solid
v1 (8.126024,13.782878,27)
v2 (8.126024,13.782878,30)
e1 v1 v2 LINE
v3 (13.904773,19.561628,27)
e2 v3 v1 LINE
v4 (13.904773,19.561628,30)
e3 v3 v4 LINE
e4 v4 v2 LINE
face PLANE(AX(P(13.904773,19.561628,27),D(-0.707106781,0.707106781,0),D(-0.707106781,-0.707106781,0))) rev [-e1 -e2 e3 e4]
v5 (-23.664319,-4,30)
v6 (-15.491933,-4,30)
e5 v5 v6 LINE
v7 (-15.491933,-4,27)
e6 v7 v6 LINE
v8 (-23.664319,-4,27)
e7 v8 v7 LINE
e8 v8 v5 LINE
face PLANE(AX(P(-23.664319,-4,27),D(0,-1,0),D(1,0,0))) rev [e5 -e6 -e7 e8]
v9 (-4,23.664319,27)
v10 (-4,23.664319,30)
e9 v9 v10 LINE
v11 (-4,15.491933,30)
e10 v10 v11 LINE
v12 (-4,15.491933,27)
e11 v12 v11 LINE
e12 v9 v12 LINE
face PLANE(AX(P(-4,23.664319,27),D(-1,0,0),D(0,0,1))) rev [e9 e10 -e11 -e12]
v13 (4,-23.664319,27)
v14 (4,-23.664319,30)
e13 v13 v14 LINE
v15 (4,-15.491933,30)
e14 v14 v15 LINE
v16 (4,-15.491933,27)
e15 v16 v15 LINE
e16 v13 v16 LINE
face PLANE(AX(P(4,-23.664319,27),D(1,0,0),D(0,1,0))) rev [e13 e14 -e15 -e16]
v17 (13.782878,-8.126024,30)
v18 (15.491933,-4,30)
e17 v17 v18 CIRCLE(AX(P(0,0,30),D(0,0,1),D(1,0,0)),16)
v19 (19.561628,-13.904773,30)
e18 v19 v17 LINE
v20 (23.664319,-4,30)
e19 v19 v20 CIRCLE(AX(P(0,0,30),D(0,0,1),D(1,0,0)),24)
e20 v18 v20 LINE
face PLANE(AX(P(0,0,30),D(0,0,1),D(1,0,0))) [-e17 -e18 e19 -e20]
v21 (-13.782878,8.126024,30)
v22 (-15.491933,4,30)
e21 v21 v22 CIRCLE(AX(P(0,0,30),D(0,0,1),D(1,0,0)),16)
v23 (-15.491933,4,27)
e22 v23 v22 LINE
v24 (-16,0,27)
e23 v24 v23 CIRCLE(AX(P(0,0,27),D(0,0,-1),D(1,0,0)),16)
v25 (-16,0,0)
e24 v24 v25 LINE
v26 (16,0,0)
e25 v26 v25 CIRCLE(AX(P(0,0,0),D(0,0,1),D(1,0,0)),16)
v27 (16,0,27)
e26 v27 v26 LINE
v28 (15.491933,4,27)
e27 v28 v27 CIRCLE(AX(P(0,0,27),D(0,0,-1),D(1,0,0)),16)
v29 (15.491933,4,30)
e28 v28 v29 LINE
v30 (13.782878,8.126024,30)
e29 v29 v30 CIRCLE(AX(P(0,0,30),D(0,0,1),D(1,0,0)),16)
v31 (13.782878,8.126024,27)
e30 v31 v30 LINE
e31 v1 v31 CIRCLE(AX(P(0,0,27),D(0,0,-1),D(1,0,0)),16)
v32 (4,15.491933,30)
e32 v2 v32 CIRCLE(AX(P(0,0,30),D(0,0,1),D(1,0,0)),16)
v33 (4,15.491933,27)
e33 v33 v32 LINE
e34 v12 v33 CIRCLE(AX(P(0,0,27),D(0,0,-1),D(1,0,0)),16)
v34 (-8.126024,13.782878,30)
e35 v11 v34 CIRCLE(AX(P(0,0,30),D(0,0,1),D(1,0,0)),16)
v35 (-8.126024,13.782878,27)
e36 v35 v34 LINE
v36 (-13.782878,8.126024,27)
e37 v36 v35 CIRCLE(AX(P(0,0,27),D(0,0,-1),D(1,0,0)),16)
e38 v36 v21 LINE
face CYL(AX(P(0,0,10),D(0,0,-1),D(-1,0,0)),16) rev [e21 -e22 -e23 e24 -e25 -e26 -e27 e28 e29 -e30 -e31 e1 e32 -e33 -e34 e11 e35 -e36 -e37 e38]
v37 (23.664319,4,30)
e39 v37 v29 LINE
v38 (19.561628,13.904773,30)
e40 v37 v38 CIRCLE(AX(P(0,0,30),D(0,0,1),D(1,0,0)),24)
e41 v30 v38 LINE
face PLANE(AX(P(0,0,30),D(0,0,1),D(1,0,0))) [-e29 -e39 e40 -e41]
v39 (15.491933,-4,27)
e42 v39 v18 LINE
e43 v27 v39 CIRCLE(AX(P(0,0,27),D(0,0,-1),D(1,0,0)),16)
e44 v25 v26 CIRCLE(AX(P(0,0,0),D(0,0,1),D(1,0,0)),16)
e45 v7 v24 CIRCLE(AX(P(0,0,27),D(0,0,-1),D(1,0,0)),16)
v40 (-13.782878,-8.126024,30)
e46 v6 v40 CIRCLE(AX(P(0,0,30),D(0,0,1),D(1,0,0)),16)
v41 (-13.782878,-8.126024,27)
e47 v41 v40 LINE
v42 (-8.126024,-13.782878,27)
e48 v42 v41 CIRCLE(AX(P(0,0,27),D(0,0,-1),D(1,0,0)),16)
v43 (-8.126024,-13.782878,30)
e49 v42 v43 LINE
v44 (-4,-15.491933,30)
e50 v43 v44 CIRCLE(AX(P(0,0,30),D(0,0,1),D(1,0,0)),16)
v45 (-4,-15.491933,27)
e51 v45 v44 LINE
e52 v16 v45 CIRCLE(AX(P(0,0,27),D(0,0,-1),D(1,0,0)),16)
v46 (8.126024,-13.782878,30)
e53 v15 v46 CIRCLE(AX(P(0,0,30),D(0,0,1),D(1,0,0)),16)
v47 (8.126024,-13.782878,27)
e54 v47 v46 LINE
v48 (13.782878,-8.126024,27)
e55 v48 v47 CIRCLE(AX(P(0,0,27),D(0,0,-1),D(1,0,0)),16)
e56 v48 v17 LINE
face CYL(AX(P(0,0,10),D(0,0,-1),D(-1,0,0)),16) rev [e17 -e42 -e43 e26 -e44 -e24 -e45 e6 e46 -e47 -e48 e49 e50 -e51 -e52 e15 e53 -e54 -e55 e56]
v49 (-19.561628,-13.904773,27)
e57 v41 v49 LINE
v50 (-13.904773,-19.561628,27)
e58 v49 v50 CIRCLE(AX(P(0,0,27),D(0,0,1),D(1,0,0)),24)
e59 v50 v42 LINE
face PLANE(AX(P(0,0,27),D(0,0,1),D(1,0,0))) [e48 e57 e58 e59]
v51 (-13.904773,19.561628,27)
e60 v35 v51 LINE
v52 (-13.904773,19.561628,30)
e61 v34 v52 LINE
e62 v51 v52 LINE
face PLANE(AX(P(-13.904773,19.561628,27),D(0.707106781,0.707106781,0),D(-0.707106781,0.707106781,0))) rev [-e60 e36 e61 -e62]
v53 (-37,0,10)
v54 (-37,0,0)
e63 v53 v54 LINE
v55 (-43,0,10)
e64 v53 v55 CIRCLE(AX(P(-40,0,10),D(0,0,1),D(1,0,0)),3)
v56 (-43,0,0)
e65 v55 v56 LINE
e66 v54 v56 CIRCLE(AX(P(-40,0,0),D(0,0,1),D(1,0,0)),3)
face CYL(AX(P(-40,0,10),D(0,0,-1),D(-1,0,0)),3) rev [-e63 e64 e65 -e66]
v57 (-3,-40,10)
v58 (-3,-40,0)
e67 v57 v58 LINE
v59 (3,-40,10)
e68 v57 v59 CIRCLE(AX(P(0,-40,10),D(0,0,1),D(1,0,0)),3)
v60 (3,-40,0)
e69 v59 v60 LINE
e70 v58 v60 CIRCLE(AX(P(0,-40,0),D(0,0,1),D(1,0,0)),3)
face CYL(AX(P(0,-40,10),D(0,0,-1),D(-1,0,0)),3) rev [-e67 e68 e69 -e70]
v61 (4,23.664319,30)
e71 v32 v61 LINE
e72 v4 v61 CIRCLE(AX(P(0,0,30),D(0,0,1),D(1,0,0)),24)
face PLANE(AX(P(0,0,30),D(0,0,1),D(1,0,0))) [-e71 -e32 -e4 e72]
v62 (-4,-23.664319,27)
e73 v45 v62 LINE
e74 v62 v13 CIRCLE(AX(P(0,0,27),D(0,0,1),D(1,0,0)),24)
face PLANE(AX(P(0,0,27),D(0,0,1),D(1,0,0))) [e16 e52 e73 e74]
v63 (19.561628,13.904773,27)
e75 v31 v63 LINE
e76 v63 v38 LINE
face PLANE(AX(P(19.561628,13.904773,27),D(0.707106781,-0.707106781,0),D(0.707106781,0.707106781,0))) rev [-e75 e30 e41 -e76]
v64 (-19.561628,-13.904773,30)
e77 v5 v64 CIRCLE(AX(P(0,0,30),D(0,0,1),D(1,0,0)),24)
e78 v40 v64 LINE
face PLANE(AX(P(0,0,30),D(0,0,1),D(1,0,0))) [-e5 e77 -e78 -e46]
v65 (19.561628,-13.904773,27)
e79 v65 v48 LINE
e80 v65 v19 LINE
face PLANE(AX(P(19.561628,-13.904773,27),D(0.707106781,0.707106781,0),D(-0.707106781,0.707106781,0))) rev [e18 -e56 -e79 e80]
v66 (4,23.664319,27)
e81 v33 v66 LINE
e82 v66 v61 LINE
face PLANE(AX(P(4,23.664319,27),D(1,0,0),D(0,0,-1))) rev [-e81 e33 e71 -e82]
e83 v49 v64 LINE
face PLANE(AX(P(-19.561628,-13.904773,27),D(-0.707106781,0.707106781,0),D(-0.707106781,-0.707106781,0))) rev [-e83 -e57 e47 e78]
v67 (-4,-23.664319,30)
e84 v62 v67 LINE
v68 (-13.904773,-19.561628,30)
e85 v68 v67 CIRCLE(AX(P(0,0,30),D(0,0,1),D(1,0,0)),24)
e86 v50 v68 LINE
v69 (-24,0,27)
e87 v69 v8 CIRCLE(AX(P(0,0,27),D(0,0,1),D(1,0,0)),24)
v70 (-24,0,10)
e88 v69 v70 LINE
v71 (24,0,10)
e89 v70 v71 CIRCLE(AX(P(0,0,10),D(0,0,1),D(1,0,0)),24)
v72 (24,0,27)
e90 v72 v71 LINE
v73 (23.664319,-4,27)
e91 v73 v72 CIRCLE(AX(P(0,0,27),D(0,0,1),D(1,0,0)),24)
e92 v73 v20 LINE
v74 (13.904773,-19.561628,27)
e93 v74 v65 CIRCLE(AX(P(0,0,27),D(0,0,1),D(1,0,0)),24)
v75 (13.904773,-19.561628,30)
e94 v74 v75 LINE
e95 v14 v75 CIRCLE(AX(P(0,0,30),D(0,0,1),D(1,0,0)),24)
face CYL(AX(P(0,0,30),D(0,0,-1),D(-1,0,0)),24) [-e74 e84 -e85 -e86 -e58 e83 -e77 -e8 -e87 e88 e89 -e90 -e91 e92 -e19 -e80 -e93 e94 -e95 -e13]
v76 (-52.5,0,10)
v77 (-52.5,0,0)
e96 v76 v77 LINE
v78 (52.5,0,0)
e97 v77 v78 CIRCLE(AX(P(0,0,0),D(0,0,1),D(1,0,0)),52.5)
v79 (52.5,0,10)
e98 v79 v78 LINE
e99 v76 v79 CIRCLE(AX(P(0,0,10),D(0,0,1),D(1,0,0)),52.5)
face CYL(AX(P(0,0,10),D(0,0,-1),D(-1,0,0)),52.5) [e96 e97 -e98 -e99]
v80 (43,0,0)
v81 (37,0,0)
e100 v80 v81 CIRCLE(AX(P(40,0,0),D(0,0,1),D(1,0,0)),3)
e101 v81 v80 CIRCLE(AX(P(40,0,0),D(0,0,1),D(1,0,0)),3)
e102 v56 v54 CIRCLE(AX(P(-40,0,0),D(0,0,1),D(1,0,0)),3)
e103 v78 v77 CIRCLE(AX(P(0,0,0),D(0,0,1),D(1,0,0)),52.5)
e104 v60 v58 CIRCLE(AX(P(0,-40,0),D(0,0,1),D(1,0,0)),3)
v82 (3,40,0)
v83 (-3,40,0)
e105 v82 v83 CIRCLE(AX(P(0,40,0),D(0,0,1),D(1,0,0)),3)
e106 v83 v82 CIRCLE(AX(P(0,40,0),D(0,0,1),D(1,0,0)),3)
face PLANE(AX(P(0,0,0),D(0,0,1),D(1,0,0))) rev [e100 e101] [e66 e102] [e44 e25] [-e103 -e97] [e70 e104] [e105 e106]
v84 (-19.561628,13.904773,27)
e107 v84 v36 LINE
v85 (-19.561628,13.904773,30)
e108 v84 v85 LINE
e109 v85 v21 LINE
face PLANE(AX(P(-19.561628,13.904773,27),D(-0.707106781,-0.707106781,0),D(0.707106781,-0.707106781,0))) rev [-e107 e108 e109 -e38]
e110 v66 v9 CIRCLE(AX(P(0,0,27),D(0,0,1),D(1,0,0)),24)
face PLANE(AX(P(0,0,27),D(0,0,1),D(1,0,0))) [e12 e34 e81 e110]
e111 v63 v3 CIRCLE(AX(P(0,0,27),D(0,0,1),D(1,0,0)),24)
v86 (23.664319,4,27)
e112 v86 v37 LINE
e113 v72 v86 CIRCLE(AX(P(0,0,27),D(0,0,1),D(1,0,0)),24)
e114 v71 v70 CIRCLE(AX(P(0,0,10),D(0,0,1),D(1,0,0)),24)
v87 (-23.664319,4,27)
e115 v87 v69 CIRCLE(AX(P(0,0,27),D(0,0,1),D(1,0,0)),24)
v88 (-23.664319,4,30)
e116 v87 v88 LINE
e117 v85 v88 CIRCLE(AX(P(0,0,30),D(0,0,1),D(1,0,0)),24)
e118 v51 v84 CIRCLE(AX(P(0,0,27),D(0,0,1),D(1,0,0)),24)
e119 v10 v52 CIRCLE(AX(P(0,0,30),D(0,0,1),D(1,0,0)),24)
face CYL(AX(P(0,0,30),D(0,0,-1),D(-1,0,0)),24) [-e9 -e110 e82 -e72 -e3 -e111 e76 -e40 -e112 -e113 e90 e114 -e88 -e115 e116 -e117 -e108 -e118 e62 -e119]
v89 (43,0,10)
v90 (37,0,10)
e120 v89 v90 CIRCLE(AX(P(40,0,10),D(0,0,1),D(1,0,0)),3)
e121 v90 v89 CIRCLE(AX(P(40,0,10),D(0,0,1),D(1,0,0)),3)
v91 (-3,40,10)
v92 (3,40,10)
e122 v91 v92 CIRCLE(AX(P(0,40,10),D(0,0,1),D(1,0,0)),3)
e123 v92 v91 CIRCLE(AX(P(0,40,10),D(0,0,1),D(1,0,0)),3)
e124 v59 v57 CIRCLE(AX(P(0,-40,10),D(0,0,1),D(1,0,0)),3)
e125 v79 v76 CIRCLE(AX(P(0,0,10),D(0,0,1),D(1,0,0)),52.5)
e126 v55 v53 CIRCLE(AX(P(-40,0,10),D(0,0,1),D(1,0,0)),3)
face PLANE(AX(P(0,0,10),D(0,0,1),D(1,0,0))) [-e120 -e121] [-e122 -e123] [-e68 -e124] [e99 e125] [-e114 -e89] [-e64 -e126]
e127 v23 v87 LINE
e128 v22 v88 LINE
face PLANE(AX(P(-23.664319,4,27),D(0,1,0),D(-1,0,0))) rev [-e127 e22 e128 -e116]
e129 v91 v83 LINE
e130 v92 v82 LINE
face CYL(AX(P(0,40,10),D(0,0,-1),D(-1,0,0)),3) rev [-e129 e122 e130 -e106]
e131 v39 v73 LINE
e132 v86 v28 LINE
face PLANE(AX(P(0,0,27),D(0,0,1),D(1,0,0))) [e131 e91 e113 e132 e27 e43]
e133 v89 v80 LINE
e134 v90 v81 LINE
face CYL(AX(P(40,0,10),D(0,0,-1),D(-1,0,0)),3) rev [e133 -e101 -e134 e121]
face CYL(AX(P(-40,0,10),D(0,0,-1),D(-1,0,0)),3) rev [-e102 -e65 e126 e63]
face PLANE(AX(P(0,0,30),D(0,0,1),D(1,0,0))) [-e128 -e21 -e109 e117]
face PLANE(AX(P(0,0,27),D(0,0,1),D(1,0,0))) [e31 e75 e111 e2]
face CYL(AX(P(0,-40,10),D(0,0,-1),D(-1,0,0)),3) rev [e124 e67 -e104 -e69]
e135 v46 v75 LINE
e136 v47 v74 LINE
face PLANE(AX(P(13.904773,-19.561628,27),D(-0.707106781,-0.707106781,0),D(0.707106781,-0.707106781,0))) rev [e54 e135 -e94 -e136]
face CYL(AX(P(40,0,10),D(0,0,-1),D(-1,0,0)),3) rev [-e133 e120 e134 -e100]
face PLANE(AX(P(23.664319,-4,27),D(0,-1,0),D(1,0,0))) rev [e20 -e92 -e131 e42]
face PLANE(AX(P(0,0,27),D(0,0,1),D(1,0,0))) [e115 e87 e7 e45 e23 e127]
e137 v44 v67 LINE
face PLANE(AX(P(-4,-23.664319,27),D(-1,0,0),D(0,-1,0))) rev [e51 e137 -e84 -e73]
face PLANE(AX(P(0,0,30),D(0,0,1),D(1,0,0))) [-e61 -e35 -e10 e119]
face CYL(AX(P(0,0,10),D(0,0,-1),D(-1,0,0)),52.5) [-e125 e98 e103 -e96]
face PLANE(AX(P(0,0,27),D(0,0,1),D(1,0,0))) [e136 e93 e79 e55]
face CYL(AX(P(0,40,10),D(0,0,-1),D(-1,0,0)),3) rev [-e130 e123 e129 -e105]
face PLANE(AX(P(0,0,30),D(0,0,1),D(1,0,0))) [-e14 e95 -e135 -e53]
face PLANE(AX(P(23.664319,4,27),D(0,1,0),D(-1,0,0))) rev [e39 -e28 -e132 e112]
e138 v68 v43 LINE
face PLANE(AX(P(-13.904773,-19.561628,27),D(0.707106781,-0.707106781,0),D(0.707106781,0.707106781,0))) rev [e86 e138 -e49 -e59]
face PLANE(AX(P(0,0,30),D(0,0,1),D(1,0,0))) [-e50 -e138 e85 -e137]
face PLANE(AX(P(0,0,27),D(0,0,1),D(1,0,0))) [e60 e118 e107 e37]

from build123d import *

# Parameters (mm, degrees)
SKETCH_1_R          = 52.5
SKETCH_1_R_2        = 16
SKETCH_1_R_3        = 3
EXTRUDE_1_DEPTH     = 10
SKETCH_2_R          = 24
SKETCH_2_R_2        = 16
EXTRUDE_2_DEPTH     = 20
CUT_EXTRUDE_START   = -3
CUT_EXTRUDE_2_DEPTH = 3


with BuildPart() as part:
    # 草图1 → 凸台-拉伸1 (new body)
    with BuildSketch(Plane.XY):
        Circle(SKETCH_1_R)
        Circle(SKETCH_1_R_2, mode=Mode.SUBTRACT)
        with Locations((0, 40)):
            Circle(SKETCH_1_R_3, mode=Mode.SUBTRACT)
        with Locations((40, 0)):
            Circle(SKETCH_1_R_3, mode=Mode.SUBTRACT)
        with Locations((0, -40)):
            Circle(SKETCH_1_R_3, mode=Mode.SUBTRACT)
        with Locations((-40, 0)):
            Circle(SKETCH_1_R_3, mode=Mode.SUBTRACT)
    extrude(amount=EXTRUDE_1_DEPTH)

    # 草图2 → 凸台-拉伸2 (add)
    with BuildSketch(Plane.XY.offset(10)):
        Circle(SKETCH_2_R)
        Circle(SKETCH_2_R_2, mode=Mode.SUBTRACT)
    extrude(amount=EXTRUDE_2_DEPTH)

    # 草图3 → 切除-拉伸2 (cut)
    with BuildSketch(Plane.XY.offset(30).offset(CUT_EXTRUDE_START)):
        with BuildLine():
            Line((-4, 23.664319132), (-4, 15.491933385))
            ThreePointArc((-4, 15.491933385), (0, 16), (4, 15.491933385))
            Line((4, 15.491933385), (4, 23.664319132))
            ThreePointArc((4, 23.664319132), (0, 24), (-4, 23.664319132))
        make_face()
        with BuildLine():
            Line((13.904773406, 19.561627655), (8.126024025, 13.782878275))
            ThreePointArc((8.126024025, 13.782878275), (11.313708499, 11.313708499), (13.782878275, 8.126024025))
            Line((13.782878275, 8.126024025), (19.561627655, 13.904773406))
            ThreePointArc((19.561627655, 13.904773406), (16.970562748, 16.970562748), (13.904773406, 19.561627655))
        make_face()
        with BuildLine():
            Line((23.664319132, 4), (15.491933385, 4))
            ThreePointArc((15.491933385, 4), (16, 0), (15.491933385, -4))
            Line((15.491933385, -4), (23.664319132, -4))
            ThreePointArc((23.664319132, -4), (24, 0), (23.664319132, 4))
        make_face()
        with BuildLine():
            Line((19.561627655, -13.904773406), (13.782878275, -8.126024025))
            ThreePointArc((13.782878275, -8.126024025), (11.313708499, -11.313708499), (8.126024025, -13.782878275))
            Line((8.126024025, -13.782878275), (13.904773406, -19.561627655))
            ThreePointArc((13.904773406, -19.561627655), (16.970562748, -16.970562748), (19.561627655, -13.904773406))
        make_face()
        with BuildLine():
            Line((4, -23.664319132), (4, -15.491933385))
            ThreePointArc((4, -15.491933385), (0, -16), (-4, -15.491933385))
            Line((-4, -15.491933385), (-4, -23.664319132))
            ThreePointArc((-4, -23.664319132), (0, -24), (4, -23.664319132))
        make_face()
        with BuildLine():
            Line((-13.904773406, -19.561627655), (-8.126024025, -13.782878275))
            ThreePointArc((-8.126024025, -13.782878275), (-11.313708499, -11.313708499), (-13.782878275, -8.126024025))
            Line((-13.782878275, -8.126024025), (-19.561627655, -13.904773406))
            ThreePointArc((-19.561627655, -13.904773406), (-16.970562748, -16.970562748), (-13.904773406, -19.561627655))
        make_face()
        with BuildLine():
            Line((-23.664319132, -4), (-15.491933385, -4))
            ThreePointArc((-15.491933385, -4), (-16, 0), (-15.491933385, 4))
            Line((-15.491933385, 4), (-23.664319132, 4))
            ThreePointArc((-23.664319132, 4), (-24, 0), (-23.664319132, -4))
        make_face()
        with BuildLine():
            Line((-19.561627655, 13.904773406), (-13.782878275, 8.126024025))
            ThreePointArc((-13.782878275, 8.126024025), (-11.313708499, 11.313708499), (-8.126024025, 13.782878275))
            Line((-8.126024025, 13.782878275), (-13.904773406, 19.561627655))
            ThreePointArc((-13.904773406, 19.561627655), (-16.970562748, 16.970562748), (-19.561627655, 13.904773406))
        make_face()
    extrude(amount=CUT_EXTRUDE_2_DEPTH, mode=Mode.SUBTRACT)


solid = part.part
